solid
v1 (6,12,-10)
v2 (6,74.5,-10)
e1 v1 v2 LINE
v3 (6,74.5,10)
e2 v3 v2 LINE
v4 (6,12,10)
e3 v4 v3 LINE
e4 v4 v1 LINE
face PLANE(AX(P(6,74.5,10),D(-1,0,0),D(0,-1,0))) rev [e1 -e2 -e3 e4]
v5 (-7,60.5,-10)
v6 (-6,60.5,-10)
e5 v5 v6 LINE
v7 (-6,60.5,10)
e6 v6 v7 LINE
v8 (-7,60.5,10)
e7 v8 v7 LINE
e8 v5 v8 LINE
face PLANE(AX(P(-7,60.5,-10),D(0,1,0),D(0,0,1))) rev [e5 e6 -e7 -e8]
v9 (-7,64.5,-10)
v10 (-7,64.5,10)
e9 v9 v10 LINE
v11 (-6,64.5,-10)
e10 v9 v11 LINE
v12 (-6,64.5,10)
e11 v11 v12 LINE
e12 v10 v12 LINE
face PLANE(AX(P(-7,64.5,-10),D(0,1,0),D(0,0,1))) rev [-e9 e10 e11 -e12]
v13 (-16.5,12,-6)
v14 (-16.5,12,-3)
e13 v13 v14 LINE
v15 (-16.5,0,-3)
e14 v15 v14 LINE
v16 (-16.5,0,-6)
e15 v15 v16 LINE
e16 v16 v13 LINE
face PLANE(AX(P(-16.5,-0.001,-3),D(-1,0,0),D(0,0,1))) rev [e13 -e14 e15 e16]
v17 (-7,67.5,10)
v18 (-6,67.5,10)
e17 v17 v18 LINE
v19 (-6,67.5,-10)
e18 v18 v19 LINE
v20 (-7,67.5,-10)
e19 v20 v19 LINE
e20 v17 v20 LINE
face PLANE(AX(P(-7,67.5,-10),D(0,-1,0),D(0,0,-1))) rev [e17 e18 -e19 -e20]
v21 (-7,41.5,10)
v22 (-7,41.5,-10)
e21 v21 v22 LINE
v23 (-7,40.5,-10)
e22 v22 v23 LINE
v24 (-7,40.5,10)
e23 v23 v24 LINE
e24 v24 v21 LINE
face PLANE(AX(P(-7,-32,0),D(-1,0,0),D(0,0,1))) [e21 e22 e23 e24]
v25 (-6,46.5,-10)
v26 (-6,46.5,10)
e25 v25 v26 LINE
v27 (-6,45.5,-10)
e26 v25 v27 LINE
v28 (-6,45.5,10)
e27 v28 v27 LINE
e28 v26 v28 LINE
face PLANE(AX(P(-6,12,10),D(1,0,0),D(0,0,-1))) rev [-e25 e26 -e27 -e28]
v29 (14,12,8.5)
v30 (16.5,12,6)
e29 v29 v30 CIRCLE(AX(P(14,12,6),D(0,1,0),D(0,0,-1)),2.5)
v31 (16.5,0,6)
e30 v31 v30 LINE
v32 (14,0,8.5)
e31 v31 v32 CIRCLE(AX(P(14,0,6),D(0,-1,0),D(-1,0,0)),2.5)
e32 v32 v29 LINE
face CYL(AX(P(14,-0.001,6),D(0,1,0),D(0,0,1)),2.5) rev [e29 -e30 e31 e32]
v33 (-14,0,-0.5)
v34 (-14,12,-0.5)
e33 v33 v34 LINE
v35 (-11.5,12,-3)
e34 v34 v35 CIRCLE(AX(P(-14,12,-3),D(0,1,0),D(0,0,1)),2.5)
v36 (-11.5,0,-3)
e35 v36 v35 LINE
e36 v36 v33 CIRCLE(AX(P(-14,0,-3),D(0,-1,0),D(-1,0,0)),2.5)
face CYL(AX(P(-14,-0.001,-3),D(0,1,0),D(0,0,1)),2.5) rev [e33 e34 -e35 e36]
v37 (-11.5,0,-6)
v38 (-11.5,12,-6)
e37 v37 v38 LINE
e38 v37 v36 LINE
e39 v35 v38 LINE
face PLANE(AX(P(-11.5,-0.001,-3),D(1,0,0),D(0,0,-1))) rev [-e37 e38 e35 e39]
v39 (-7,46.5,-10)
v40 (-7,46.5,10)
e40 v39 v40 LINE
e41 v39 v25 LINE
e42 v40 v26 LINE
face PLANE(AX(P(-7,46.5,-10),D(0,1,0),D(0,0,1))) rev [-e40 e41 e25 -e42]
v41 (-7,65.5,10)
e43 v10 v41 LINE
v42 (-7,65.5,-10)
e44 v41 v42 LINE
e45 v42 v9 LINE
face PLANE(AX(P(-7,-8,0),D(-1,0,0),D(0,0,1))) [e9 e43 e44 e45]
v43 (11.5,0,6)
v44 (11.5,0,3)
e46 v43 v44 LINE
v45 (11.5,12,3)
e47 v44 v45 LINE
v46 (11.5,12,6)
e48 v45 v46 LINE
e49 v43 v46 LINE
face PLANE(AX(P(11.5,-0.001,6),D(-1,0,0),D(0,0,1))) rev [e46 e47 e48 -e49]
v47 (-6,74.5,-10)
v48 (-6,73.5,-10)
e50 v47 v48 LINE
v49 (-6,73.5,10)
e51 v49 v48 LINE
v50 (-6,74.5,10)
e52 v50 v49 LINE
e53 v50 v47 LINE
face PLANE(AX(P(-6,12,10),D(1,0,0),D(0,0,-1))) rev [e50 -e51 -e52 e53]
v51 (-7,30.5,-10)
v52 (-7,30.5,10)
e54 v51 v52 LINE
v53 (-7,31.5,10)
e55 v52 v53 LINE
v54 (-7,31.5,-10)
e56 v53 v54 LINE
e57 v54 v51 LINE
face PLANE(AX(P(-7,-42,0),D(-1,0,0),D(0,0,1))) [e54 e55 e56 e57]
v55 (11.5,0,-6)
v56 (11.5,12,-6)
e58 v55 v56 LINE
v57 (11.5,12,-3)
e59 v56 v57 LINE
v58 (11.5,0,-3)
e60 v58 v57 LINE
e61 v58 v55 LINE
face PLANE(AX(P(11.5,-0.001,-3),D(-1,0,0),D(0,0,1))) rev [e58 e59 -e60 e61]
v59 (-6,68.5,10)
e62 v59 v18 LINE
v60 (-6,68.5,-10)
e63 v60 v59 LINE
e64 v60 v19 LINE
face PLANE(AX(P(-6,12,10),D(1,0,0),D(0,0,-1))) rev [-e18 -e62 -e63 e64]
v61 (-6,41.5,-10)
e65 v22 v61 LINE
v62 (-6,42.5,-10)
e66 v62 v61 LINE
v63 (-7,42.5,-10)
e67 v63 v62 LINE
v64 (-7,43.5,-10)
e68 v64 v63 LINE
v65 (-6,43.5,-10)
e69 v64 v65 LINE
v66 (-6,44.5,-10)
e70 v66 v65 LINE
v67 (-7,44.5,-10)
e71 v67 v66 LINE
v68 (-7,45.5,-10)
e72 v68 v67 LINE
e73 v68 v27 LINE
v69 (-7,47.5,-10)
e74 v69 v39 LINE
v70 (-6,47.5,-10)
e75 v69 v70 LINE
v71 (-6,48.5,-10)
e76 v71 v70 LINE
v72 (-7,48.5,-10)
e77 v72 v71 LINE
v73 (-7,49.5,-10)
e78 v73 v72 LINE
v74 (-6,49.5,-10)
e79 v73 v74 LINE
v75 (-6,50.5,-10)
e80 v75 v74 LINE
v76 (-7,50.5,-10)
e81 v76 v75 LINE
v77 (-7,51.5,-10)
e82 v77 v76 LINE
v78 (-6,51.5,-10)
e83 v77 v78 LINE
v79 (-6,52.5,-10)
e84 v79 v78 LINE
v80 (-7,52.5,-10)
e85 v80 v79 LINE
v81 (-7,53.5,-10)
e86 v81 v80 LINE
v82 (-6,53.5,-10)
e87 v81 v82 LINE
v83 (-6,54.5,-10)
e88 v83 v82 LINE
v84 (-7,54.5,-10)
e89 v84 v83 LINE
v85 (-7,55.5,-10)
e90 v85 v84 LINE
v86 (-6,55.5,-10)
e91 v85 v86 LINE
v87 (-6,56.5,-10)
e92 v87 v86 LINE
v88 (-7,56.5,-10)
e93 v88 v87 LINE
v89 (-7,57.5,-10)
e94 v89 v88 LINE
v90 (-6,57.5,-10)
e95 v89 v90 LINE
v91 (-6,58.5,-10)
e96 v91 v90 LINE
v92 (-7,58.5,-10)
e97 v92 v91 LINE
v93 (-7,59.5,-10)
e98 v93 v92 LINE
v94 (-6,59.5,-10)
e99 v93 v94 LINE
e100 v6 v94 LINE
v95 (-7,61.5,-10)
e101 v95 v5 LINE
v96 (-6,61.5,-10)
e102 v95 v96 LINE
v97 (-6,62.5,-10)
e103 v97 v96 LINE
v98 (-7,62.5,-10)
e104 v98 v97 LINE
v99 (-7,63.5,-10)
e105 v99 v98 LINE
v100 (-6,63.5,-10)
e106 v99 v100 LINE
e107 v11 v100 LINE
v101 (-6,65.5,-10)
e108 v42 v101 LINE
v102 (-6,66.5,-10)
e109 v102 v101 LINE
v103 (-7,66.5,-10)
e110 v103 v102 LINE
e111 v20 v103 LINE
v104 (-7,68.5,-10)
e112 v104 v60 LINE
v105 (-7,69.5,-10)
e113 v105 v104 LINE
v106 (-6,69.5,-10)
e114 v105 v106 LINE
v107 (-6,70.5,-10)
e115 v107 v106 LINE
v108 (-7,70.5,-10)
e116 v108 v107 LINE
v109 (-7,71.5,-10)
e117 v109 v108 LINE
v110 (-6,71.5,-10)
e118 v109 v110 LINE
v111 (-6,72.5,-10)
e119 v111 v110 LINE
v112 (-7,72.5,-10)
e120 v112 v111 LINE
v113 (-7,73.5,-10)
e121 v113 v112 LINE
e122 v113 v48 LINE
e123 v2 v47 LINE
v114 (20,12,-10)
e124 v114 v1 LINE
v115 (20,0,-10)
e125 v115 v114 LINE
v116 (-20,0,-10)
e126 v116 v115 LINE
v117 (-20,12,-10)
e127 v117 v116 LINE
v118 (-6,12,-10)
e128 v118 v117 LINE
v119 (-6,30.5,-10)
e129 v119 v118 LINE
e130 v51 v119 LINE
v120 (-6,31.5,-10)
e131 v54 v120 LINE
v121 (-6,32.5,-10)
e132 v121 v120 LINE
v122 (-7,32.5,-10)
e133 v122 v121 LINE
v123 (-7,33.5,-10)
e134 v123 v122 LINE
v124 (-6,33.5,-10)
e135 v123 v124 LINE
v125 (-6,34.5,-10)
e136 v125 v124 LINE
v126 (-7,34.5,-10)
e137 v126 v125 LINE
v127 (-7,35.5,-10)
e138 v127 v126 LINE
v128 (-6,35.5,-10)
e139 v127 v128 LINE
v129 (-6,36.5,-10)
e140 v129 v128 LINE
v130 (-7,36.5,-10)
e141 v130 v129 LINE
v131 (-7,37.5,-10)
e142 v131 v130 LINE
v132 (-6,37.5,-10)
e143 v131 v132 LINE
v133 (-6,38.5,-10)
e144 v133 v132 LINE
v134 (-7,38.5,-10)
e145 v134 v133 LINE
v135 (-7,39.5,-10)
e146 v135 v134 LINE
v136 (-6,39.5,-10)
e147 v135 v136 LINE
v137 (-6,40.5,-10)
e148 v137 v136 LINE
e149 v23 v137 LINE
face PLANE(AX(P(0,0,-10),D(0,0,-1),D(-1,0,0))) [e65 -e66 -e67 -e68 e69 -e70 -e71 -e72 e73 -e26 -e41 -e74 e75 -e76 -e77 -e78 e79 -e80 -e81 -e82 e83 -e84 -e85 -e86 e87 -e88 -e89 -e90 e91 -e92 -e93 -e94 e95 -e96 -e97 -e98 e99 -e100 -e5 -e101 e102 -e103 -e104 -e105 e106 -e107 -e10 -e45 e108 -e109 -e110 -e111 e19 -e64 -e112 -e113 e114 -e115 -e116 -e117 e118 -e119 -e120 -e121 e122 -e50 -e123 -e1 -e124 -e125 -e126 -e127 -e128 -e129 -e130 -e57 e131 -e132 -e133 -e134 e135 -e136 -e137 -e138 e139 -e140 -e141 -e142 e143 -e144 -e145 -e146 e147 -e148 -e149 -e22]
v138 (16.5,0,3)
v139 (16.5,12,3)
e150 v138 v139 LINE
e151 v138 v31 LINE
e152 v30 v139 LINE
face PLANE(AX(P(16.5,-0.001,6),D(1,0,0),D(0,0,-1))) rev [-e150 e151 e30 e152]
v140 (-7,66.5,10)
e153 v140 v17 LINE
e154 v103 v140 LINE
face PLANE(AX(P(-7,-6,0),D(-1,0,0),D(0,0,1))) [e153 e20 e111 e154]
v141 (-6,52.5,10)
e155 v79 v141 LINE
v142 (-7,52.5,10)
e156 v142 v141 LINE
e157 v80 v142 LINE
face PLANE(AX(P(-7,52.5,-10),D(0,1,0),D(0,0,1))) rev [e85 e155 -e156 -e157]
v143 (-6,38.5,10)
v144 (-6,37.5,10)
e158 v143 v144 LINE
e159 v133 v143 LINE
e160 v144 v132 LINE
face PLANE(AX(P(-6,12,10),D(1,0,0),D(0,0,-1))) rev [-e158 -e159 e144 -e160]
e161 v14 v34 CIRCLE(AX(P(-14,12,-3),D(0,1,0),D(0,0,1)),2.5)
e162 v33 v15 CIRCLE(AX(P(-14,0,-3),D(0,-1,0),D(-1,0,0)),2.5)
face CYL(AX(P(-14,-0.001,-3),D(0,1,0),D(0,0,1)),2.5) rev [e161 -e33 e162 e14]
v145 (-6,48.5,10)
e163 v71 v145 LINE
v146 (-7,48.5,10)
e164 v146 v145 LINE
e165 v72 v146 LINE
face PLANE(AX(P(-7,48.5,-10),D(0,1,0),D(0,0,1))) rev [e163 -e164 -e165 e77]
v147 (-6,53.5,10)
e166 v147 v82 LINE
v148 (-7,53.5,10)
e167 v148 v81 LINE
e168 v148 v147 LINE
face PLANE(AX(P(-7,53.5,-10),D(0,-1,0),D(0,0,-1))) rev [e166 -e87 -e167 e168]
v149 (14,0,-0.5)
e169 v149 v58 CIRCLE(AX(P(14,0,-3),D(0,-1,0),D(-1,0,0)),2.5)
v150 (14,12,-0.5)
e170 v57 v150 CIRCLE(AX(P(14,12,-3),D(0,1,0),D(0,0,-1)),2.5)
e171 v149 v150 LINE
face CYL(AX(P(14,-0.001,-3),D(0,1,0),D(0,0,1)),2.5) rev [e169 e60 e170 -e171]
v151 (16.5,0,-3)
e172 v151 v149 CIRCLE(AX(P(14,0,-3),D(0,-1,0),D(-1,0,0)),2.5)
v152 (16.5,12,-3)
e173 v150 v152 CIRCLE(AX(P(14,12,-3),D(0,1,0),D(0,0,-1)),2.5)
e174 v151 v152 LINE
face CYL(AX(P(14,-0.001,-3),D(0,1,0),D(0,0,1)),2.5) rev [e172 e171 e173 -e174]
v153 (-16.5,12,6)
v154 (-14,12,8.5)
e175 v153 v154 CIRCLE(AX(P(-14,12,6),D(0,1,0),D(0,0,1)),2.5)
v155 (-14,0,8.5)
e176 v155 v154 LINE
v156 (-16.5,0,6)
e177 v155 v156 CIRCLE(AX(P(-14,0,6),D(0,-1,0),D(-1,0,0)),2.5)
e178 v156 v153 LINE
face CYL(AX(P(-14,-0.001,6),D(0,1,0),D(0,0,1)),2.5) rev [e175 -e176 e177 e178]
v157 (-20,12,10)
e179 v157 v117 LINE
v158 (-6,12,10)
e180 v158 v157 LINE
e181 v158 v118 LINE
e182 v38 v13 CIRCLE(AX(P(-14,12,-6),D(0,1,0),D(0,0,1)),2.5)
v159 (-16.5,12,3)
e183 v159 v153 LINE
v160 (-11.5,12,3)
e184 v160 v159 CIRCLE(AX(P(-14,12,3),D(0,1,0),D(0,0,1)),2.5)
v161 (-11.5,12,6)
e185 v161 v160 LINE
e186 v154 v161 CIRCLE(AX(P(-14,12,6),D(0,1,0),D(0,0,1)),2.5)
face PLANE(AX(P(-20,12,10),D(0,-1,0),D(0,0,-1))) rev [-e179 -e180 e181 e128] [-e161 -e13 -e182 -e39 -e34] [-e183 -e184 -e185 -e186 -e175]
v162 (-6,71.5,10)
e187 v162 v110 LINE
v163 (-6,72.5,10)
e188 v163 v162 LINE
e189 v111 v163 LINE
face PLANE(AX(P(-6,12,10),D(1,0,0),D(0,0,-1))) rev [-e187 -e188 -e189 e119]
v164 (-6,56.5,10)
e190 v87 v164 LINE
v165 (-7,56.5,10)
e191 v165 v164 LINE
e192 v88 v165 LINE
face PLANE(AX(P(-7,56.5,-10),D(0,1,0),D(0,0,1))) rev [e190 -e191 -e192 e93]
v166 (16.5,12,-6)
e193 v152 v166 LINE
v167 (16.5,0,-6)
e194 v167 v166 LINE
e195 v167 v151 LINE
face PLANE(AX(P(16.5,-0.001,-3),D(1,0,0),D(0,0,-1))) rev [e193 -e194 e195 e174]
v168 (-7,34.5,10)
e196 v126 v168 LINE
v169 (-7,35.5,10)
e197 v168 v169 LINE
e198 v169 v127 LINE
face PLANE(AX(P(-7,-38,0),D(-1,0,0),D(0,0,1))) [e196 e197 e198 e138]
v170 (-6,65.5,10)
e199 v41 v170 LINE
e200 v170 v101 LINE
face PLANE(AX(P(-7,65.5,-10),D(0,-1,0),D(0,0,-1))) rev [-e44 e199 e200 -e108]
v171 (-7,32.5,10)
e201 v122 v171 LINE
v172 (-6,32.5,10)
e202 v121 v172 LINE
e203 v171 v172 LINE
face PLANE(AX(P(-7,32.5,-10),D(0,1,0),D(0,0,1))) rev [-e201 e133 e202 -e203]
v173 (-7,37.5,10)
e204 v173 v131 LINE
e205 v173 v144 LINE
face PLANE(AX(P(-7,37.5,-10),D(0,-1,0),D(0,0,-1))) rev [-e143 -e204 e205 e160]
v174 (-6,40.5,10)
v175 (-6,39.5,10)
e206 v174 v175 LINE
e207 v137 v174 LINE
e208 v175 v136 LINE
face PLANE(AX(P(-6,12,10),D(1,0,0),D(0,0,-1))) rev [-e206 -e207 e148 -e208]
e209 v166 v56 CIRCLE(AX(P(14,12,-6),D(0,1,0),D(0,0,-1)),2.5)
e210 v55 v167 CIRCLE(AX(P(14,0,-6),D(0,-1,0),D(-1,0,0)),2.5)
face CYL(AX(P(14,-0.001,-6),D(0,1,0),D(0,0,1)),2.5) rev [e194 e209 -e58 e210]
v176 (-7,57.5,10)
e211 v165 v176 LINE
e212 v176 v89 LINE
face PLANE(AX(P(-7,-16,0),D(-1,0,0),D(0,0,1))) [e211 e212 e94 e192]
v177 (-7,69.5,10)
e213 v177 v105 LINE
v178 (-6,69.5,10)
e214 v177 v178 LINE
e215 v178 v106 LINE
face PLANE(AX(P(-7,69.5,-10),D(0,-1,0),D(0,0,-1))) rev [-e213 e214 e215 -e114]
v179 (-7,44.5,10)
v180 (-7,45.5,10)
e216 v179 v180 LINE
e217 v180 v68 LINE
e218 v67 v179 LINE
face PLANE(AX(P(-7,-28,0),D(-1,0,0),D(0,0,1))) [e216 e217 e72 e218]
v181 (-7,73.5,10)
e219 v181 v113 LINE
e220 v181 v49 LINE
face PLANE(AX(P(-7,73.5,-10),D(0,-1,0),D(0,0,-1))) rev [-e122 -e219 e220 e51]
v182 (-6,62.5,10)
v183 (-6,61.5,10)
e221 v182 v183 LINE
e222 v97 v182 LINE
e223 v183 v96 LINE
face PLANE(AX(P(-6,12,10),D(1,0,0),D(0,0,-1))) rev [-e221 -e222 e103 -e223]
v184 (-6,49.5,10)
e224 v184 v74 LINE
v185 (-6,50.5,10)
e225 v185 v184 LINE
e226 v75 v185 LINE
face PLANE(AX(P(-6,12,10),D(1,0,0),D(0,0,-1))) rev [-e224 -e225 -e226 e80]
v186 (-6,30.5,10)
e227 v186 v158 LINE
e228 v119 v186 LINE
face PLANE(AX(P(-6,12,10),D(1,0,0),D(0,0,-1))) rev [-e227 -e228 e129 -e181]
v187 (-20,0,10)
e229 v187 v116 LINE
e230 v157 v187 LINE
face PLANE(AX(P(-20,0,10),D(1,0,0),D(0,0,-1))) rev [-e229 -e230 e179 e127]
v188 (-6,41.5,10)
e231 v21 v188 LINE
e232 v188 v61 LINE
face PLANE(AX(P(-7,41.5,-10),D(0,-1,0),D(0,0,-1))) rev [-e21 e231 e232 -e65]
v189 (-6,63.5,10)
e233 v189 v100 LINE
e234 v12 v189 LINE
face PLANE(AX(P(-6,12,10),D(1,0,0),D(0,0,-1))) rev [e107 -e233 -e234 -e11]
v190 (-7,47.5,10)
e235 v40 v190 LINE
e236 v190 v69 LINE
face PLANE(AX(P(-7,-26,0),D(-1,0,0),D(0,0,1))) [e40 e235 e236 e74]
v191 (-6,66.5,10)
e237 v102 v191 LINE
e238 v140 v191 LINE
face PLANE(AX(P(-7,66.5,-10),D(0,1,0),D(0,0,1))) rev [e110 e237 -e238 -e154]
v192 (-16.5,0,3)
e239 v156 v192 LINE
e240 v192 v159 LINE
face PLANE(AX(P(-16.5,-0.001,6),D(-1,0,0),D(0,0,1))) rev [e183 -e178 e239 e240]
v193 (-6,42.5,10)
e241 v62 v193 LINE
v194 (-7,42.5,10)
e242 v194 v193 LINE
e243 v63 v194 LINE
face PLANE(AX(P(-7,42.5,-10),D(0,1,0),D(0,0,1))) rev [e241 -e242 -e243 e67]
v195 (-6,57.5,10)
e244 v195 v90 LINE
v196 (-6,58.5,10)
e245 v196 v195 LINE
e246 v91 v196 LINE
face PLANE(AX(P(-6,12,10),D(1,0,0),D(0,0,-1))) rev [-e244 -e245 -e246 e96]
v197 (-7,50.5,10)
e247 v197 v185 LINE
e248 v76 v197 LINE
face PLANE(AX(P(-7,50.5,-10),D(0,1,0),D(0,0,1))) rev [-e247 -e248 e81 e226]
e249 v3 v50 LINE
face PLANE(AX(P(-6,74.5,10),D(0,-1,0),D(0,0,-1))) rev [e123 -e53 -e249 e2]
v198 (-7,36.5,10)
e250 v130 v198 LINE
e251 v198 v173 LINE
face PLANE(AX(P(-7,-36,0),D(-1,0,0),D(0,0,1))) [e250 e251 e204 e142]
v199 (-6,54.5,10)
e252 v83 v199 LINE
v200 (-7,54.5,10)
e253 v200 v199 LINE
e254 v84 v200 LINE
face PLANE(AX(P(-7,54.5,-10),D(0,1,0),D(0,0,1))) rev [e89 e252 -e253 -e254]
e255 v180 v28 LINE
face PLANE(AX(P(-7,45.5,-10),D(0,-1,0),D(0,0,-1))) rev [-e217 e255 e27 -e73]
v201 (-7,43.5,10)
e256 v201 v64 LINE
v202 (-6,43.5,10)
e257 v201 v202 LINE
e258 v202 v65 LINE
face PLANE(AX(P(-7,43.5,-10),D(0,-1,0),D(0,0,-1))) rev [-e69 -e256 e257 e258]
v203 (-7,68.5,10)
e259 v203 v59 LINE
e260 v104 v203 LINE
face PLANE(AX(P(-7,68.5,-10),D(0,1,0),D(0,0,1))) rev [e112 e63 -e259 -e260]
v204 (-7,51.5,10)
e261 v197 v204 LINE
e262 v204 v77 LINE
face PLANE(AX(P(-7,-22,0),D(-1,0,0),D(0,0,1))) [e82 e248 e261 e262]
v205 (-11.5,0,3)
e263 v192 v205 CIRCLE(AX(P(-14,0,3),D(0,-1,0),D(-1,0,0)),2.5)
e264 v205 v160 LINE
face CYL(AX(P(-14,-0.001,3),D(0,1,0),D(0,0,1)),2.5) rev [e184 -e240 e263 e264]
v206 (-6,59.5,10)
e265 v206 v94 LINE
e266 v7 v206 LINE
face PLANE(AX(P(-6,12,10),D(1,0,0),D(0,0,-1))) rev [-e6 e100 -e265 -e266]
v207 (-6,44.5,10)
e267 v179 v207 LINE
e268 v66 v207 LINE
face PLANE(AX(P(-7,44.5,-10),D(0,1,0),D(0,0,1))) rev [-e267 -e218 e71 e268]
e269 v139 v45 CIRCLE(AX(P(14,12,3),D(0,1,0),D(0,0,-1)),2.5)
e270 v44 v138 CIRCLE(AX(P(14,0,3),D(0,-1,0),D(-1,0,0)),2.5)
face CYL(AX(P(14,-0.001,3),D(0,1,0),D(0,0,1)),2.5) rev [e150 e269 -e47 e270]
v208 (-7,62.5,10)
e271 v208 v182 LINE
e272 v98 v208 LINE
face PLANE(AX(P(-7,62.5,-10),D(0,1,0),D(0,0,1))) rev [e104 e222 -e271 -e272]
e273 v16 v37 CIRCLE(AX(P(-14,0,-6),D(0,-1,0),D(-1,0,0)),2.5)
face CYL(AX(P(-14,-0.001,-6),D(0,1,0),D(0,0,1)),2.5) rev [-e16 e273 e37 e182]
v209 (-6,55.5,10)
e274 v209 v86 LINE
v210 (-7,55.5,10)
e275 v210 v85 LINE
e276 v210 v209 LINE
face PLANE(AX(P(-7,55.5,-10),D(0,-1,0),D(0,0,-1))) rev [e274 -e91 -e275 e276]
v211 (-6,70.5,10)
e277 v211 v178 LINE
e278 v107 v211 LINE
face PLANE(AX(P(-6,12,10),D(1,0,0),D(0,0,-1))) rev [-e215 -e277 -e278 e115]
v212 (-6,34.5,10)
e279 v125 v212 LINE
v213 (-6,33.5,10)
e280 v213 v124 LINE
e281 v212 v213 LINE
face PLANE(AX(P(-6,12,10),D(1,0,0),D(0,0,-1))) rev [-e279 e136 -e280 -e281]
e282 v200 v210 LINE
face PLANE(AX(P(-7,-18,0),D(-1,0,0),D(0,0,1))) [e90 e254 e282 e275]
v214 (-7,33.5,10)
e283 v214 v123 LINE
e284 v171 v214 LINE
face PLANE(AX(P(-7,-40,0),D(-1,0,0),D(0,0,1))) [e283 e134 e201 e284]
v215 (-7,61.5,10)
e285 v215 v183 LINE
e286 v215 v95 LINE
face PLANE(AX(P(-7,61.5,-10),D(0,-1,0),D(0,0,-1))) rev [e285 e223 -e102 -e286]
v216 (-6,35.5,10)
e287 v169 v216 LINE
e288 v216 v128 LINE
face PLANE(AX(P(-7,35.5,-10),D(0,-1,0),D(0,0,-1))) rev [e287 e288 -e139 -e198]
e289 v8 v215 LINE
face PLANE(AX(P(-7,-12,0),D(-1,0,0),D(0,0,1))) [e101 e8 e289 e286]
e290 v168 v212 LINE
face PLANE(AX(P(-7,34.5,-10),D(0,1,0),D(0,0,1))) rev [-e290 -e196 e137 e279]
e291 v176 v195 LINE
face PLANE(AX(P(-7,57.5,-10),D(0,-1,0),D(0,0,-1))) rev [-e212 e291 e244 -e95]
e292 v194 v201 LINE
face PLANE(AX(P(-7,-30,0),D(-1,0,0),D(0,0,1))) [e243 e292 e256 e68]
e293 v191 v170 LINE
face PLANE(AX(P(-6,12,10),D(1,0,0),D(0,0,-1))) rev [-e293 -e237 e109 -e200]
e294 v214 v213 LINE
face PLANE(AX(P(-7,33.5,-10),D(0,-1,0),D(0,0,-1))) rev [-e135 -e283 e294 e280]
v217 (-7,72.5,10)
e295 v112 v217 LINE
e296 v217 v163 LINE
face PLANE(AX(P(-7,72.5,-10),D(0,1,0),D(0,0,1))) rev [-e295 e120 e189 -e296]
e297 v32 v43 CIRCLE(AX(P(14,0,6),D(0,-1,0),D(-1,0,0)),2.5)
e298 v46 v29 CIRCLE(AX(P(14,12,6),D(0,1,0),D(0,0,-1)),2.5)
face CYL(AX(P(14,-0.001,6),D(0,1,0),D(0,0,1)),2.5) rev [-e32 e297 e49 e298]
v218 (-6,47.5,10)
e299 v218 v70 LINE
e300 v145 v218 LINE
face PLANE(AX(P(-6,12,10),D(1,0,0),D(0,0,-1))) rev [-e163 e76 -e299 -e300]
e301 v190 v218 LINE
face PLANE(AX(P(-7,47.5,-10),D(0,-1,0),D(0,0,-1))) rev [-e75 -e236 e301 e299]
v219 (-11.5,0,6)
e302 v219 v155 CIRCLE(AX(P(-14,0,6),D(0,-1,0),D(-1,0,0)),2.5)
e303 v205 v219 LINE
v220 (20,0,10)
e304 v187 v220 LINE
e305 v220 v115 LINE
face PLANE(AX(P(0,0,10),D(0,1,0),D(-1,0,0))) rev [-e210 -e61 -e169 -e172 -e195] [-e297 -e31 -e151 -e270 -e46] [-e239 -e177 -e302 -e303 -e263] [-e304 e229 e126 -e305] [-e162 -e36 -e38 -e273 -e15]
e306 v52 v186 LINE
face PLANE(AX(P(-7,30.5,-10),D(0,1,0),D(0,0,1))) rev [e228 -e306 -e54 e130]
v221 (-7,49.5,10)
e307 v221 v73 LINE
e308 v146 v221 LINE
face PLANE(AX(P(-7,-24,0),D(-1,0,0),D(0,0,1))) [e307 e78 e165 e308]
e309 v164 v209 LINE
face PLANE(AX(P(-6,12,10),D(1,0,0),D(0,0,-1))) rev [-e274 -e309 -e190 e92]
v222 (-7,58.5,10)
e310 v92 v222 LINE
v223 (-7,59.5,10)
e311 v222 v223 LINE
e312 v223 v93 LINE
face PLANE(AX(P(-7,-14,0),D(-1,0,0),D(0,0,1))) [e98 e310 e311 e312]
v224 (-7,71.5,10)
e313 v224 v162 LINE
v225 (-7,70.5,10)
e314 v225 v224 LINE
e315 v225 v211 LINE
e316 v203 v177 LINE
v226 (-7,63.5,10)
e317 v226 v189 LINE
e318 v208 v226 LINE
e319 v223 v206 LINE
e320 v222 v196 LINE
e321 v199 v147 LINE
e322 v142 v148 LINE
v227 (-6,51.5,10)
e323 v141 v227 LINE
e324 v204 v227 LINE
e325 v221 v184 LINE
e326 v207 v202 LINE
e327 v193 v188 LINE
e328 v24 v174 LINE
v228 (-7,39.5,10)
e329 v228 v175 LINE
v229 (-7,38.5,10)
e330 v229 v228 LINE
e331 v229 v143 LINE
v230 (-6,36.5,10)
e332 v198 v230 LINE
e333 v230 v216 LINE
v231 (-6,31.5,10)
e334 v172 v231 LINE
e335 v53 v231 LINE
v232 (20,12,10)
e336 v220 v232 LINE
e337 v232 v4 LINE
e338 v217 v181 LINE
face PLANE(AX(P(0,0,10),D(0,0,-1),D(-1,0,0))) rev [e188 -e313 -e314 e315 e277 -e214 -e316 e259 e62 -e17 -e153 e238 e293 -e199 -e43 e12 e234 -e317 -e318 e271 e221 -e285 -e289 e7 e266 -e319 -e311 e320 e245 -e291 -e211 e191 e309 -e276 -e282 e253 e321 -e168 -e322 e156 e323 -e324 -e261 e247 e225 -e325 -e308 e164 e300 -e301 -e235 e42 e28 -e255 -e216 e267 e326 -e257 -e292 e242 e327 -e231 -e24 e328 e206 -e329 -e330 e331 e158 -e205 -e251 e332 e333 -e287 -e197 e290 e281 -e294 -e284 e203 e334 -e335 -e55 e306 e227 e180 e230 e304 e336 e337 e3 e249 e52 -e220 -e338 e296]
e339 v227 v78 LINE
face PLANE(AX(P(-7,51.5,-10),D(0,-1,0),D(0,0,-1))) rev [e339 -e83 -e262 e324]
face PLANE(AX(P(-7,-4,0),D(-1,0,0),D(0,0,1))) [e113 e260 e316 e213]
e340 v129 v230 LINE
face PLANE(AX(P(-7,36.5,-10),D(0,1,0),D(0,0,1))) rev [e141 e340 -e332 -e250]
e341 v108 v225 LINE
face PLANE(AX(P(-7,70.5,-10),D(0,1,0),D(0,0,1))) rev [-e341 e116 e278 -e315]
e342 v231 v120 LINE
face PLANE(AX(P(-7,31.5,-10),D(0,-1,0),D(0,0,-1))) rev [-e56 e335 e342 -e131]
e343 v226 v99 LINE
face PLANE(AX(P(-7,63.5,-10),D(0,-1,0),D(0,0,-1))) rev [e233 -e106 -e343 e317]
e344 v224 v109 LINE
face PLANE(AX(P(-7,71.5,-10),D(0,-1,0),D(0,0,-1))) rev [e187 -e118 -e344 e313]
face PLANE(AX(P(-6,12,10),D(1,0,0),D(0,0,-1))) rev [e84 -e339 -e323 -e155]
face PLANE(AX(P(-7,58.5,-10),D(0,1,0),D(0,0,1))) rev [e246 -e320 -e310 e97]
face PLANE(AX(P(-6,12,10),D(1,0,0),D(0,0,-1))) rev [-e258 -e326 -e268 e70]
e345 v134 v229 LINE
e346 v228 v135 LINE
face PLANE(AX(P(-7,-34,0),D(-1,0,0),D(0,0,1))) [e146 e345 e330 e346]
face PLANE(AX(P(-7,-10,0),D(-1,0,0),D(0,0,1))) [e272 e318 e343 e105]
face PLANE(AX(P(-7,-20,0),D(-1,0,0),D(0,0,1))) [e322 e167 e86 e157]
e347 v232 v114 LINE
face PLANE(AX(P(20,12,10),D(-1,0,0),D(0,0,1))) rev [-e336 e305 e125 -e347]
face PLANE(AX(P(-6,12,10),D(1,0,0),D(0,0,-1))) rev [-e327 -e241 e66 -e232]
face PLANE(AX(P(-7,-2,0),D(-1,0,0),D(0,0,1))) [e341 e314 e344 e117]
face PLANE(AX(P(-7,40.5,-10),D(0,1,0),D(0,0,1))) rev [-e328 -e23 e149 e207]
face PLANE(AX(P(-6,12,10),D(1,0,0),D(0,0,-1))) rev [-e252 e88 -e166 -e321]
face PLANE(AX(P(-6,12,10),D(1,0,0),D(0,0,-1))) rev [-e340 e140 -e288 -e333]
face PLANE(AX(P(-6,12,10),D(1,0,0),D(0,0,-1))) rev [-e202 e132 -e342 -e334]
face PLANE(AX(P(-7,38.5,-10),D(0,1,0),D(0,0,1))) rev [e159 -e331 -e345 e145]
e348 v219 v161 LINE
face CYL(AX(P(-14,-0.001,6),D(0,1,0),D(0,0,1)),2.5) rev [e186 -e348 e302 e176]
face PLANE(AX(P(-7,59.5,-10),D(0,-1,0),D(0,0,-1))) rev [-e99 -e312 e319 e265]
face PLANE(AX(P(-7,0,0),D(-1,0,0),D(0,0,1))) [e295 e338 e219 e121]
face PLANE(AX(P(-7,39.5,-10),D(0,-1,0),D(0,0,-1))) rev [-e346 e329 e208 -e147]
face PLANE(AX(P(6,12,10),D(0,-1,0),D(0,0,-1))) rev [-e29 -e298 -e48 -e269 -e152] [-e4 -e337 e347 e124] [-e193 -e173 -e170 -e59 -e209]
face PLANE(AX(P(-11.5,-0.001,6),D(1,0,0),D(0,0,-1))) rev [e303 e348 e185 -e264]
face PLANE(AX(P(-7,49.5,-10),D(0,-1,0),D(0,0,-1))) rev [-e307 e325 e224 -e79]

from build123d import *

# Parameters (mm, degrees)
EXTRUDE_1_DEPTH        = 10
CUT_EXTRUDE_1_REACH    = 68.38
SKETCH_3_W             = 20
SKETCH_3_H             = 1
EXTRUDE_2_DEPTH        = 1
PATTERN_LINEAR_1_COUNT = 22
PATTERN_LINEAR_1_PITCH = 2


with BuildPart() as part:
    # 草图1 → 凸台-拉伸1 (new, symmetric)
    with BuildSketch(Plane.XY):
        Polygon((0, 0), (-20, 0), (-20, 12), (-6, 12), (-6, 74.5), (6, 74.5), (6, 12), (20, 12), (20, 0), align=None)
    extrude(amount=EXTRUDE_1_DEPTH, both=True)

    # 草图2 → 切除-拉伸1 (cut, up to next)
    with BuildSketch(Plane(origin=(0, 12, 0), x_dir=(1, 0, 0), z_dir=(0, 1, 0)), mode=Mode.PRIVATE) as cut_extrude_1_sk1:
        with BuildLine():
            Line((-16.5, 3), (-16.5, 6))
            ThreePointArc((-16.5, 6), (-14, 8.5), (-11.5, 6))
            Line((-11.5, 6), (-11.5, 3))
            ThreePointArc((-11.5, 3), (-14, 0.5), (-16.5, 3))
        make_face()
    cut_extrude_1_tool1 = extrude(cut_extrude_1_sk1.sketch, amount=-CUT_EXTRUDE_1_REACH, mode=Mode.PRIVATE) & part.part
    # 草图2 → 切除-拉伸1 (cut, up to next)
    with BuildSketch(Plane(origin=(0, 12, 0), x_dir=(1, 0, 0), z_dir=(0, 1, 0)), mode=Mode.PRIVATE) as cut_extrude_1_sk2:
        with BuildLine():
            Line((-16.5, -6), (-16.5, -3))
            ThreePointArc((-16.5, -3), (-14, -0.5), (-11.5, -3))
            Line((-11.5, -3), (-11.5, -6))
            ThreePointArc((-11.5, -6), (-14, -8.5), (-16.5, -6))
        make_face()
    cut_extrude_1_tool2 = extrude(cut_extrude_1_sk2.sketch, amount=-CUT_EXTRUDE_1_REACH, mode=Mode.PRIVATE) & part.part
    # 草图2 → 切除-拉伸1 (cut, up to next)
    with BuildSketch(Plane(origin=(0, 12, 0), x_dir=(1, 0, 0), z_dir=(0, 1, 0)), mode=Mode.PRIVATE) as cut_extrude_1_sk3:
        with BuildLine():
            Line((16.5, -6), (16.5, -3))
            ThreePointArc((16.5, -3), (14, -0.5), (11.5, -3))
            Line((11.5, -3), (11.5, -6))
            ThreePointArc((11.5, -6), (14, -8.5), (16.5, -6))
        make_face()
    cut_extrude_1_tool3 = extrude(cut_extrude_1_sk3.sketch, amount=-CUT_EXTRUDE_1_REACH, mode=Mode.PRIVATE) & part.part
    # 草图2 → 切除-拉伸1 (cut, up to next)
    with BuildSketch(Plane(origin=(0, 12, 0), x_dir=(1, 0, 0), z_dir=(0, 1, 0)), mode=Mode.PRIVATE) as cut_extrude_1_sk4:
        with BuildLine():
            Line((16.5, 3), (16.5, 6))
            ThreePointArc((16.5, 6), (14, 8.5), (11.5, 6))
            Line((11.5, 6), (11.5, 3))
            ThreePointArc((11.5, 3), (14, 0.5), (16.5, 3))
        make_face()
    cut_extrude_1_tool4 = extrude(cut_extrude_1_sk4.sketch, amount=-CUT_EXTRUDE_1_REACH, mode=Mode.PRIVATE) & part.part
    add(cut_extrude_1_tool1.solids().sort_by_distance((-14, 12, -4.5))[0], mode=Mode.SUBTRACT)
    add(cut_extrude_1_tool2.solids().sort_by_distance((-14, 12, 4.5))[0], mode=Mode.SUBTRACT)
    add(cut_extrude_1_tool3.solids().sort_by_distance((14, 12, 4.5))[0], mode=Mode.SUBTRACT)
    add(cut_extrude_1_tool4.solids().sort_by_distance((14, 12, -4.5))[0], mode=Mode.SUBTRACT)

    # 草图3 → 凸台-拉伸2 (add)
    with BuildSketch(Plane.ZY.offset(6)):
        with Locations((0, 73)):
            Rectangle(SKETCH_3_W, SKETCH_3_H)
    extrude_2 = extrude(amount=EXTRUDE_2_DEPTH)

    # 阵列(线性)1: 凸台-拉伸2 ×22
    with Locations(*[(0, -i * PATTERN_LINEAR_1_PITCH, 0) for i in range(1, PATTERN_LINEAR_1_COUNT)]):
        add(extrude_2)


solid = part.part
